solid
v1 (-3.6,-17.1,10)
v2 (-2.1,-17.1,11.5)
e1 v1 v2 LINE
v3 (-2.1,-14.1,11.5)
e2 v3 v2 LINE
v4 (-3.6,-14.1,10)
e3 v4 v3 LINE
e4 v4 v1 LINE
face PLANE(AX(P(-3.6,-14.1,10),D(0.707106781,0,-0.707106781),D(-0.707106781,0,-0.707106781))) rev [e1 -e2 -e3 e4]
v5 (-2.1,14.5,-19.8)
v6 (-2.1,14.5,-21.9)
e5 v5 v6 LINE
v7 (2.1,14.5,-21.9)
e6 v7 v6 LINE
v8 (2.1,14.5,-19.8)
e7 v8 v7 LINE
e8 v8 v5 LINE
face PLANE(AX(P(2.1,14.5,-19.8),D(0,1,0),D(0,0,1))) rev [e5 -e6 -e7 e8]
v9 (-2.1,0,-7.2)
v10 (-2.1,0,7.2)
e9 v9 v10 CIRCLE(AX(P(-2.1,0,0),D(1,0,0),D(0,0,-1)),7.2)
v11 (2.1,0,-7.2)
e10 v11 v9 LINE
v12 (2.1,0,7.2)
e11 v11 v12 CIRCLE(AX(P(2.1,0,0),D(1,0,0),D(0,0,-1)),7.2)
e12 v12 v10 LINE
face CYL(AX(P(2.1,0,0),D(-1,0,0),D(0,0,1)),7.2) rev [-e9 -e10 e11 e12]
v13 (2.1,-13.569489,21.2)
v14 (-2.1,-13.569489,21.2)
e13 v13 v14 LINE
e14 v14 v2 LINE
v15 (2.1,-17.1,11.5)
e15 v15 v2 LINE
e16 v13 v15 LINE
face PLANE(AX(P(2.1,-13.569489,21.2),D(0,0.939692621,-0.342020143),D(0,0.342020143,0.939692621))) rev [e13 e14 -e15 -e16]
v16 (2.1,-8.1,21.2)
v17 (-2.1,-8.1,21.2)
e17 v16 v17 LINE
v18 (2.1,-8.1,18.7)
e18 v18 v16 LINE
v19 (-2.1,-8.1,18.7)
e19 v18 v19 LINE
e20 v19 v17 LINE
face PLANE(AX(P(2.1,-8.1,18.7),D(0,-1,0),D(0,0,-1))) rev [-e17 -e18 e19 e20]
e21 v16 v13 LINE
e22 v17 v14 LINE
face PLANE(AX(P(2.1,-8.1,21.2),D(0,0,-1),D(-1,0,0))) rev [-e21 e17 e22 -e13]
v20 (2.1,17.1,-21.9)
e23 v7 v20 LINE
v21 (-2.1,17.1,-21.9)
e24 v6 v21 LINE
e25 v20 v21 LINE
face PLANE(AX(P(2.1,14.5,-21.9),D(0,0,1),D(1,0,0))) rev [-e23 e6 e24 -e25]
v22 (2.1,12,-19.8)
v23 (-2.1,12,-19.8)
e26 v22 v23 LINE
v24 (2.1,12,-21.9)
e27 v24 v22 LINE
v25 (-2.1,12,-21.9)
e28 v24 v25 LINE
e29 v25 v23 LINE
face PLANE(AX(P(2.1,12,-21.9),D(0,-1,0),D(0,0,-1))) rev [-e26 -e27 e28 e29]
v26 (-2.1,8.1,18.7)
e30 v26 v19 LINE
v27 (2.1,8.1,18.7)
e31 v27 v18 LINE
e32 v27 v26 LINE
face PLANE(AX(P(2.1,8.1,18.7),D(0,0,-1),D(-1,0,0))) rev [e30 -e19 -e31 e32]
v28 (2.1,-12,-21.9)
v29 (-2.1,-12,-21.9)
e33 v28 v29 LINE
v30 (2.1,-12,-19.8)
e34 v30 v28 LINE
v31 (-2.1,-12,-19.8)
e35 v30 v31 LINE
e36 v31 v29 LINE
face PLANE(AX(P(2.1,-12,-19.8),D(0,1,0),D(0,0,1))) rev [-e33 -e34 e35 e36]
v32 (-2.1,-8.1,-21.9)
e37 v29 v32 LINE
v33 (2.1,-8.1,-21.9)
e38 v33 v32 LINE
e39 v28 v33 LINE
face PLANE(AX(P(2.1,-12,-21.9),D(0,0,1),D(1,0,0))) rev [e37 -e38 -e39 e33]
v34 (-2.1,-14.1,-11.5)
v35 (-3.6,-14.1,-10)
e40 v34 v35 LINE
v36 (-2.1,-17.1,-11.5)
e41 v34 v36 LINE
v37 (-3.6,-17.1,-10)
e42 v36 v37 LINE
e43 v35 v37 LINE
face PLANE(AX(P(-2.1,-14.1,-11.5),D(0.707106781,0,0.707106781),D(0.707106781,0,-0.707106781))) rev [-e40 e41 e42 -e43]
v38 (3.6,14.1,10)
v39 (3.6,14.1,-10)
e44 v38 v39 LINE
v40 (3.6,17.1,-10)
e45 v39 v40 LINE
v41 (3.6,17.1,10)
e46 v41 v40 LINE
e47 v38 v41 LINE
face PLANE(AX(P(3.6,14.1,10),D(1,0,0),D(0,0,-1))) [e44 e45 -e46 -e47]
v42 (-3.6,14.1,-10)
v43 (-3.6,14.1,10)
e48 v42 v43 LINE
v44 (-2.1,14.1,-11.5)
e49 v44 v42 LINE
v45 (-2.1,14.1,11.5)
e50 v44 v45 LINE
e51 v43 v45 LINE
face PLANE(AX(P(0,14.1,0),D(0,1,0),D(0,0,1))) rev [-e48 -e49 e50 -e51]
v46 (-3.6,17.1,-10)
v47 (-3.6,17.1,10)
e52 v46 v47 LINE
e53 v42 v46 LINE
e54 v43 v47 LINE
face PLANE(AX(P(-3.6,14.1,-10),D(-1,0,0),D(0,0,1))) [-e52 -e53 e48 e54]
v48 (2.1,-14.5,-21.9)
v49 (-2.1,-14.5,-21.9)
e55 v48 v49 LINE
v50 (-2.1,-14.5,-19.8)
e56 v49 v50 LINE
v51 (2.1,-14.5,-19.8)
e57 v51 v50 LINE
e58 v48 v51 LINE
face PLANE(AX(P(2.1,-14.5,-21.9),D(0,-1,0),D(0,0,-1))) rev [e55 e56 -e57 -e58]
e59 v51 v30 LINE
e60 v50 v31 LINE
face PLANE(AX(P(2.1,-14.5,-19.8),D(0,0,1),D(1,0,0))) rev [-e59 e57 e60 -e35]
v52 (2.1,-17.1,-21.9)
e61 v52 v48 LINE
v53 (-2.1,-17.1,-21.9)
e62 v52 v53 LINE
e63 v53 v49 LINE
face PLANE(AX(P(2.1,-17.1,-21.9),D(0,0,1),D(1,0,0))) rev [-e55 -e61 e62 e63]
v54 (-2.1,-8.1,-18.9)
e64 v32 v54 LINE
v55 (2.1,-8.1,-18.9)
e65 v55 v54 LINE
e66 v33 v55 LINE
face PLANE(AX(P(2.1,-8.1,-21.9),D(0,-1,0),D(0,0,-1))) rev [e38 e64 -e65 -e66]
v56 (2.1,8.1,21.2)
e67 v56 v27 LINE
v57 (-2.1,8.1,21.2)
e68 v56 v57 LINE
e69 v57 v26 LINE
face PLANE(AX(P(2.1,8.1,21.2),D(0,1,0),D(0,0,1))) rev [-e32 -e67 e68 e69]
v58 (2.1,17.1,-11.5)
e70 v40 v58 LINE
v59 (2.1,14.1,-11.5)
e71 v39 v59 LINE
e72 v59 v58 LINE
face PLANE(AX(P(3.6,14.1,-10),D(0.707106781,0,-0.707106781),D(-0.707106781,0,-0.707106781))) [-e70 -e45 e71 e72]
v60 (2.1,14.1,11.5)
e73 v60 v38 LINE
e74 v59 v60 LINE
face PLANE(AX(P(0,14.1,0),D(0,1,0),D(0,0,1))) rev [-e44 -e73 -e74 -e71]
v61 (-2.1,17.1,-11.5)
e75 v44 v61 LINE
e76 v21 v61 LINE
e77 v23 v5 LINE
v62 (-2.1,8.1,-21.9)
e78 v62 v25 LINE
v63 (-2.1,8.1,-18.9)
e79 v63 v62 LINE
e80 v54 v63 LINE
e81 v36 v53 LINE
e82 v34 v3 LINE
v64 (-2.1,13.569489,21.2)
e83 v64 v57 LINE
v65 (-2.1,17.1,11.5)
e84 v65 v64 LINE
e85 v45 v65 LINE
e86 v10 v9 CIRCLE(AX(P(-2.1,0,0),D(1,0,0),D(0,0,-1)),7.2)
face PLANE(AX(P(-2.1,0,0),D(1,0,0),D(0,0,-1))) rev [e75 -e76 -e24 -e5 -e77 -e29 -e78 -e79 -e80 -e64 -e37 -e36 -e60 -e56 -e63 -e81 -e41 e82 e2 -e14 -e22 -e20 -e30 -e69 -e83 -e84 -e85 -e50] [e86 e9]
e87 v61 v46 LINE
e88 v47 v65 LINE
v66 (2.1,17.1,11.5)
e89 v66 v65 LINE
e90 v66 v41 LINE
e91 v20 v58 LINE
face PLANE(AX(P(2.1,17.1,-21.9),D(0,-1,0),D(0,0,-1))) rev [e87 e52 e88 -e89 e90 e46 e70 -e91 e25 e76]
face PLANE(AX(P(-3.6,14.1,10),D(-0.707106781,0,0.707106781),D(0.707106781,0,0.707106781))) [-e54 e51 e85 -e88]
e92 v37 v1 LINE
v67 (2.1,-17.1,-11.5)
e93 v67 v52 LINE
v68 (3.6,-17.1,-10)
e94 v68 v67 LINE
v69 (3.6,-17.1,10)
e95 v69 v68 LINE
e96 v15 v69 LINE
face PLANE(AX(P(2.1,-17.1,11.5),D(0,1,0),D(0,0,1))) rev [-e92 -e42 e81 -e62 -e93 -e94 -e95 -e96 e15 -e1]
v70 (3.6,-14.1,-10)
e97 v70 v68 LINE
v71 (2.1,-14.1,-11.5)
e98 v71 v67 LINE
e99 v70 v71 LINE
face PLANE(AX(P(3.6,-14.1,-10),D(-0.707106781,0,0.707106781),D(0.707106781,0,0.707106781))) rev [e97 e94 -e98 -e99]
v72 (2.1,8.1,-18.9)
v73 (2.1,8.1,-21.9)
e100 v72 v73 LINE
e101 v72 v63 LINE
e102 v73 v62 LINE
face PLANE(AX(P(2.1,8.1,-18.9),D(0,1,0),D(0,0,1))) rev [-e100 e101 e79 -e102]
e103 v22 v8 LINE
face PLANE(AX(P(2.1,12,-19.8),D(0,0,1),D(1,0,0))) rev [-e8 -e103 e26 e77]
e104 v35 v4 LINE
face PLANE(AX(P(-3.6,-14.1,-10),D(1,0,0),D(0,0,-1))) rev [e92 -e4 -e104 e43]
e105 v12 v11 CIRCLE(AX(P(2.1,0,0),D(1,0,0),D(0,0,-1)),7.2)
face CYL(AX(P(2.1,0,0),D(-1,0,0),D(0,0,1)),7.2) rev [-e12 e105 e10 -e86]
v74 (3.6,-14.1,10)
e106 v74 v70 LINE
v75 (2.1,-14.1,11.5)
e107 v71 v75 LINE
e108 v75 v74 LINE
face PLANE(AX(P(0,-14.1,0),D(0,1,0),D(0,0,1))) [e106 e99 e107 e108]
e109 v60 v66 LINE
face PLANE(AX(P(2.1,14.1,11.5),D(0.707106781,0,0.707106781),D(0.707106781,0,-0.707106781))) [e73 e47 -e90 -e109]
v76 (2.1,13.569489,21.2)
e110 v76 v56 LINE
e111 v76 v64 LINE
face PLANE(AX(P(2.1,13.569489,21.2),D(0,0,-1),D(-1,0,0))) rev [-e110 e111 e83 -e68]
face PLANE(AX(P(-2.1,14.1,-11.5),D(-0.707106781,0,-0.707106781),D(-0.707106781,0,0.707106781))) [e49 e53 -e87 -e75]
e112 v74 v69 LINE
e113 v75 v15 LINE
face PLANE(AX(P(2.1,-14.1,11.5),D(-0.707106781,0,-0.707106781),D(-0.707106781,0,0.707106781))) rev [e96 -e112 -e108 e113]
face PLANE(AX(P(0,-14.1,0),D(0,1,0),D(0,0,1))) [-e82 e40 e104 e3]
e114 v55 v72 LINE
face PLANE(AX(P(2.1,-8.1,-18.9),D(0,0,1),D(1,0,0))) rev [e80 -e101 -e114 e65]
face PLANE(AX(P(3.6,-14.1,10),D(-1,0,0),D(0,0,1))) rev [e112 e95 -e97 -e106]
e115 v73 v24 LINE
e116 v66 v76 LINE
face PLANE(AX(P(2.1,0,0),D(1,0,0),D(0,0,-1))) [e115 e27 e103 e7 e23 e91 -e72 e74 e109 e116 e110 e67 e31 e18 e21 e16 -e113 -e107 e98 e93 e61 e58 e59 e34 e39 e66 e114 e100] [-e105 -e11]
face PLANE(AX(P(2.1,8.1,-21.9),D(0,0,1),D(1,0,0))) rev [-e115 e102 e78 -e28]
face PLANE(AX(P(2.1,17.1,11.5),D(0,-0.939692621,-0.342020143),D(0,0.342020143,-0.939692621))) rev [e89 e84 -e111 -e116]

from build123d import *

# Parameters (mm, degrees)
EXTRUDE_1_DEPTH      = 2.1
EXTRUDE_1_DEPTH_BACK = 2.1
SKETCH_1_R           = 7.2
EXTRUDE_2_DEPTH      = 3
EXTRUDE_3_DEPTH      = 3


with BuildPart() as part:
    # 草图1 → 凸台-拉伸1 (new, two sides: drawn at the far end of the back side and taken through both)
    with BuildSketch(Plane(origin=(0, 0, 0), x_dir=(0, 0, -1), z_dir=(1, 0, 0)).offset(-EXTRUDE_1_DEPTH_BACK)):
        Polygon((-21.2, 8.1), (-18.7, 8.1), (-18.7, -8.1), (-21.2, -8.1), (-21.2, -13.569488728), (-11.5, -17.1), (21.9, -17.1), (21.9, -14.5), (19.8, -14.5), (19.8, -12), (21.9, -12), (21.9, -8.1), (18.9, -8.1), (18.9, 8.1), (21.9, 8.1), (21.9, 12), (19.8, 12), (19.8, 14.5), (21.9, 14.5), (21.9, 17.1), (-11.5, 17.1), (-21.2, 13.569488728), align=None)
        Circle(SKETCH_1_R, mode=Mode.SUBTRACT)
    extrude(amount=EXTRUDE_1_DEPTH + EXTRUDE_1_DEPTH_BACK)

    # 草图2 → 凸台-拉伸2 (add)
    with BuildSketch(Plane(origin=(0, 17.1, 0), x_dir=(1, 0, 0), z_dir=(0, 1, 0))):
        Polygon((-3.6, -10), (-2.1, -11.5), (2.1, -11.5), (3.6, -10), (3.6, 10), (2.1, 11.5), (-2.1, 11.5), (-3.6, 10), align=None)
    extrude(amount=-EXTRUDE_2_DEPTH)

    # 草图3 → 凸台-拉伸3 (add)
    with BuildSketch(Plane(origin=(0, -17.1, 0), x_dir=(1, 0, 0), z_dir=(0, 1, 0))):
        Polygon((-3.6, -10), (-2.1, -11.5), (2.1, -11.5), (3.6, -10), (3.6, 10), (2.1, 11.5), (-2.1, 11.5), (-3.6, 10), align=None)
    extrude(amount=EXTRUDE_3_DEPTH)


solid = part.part
